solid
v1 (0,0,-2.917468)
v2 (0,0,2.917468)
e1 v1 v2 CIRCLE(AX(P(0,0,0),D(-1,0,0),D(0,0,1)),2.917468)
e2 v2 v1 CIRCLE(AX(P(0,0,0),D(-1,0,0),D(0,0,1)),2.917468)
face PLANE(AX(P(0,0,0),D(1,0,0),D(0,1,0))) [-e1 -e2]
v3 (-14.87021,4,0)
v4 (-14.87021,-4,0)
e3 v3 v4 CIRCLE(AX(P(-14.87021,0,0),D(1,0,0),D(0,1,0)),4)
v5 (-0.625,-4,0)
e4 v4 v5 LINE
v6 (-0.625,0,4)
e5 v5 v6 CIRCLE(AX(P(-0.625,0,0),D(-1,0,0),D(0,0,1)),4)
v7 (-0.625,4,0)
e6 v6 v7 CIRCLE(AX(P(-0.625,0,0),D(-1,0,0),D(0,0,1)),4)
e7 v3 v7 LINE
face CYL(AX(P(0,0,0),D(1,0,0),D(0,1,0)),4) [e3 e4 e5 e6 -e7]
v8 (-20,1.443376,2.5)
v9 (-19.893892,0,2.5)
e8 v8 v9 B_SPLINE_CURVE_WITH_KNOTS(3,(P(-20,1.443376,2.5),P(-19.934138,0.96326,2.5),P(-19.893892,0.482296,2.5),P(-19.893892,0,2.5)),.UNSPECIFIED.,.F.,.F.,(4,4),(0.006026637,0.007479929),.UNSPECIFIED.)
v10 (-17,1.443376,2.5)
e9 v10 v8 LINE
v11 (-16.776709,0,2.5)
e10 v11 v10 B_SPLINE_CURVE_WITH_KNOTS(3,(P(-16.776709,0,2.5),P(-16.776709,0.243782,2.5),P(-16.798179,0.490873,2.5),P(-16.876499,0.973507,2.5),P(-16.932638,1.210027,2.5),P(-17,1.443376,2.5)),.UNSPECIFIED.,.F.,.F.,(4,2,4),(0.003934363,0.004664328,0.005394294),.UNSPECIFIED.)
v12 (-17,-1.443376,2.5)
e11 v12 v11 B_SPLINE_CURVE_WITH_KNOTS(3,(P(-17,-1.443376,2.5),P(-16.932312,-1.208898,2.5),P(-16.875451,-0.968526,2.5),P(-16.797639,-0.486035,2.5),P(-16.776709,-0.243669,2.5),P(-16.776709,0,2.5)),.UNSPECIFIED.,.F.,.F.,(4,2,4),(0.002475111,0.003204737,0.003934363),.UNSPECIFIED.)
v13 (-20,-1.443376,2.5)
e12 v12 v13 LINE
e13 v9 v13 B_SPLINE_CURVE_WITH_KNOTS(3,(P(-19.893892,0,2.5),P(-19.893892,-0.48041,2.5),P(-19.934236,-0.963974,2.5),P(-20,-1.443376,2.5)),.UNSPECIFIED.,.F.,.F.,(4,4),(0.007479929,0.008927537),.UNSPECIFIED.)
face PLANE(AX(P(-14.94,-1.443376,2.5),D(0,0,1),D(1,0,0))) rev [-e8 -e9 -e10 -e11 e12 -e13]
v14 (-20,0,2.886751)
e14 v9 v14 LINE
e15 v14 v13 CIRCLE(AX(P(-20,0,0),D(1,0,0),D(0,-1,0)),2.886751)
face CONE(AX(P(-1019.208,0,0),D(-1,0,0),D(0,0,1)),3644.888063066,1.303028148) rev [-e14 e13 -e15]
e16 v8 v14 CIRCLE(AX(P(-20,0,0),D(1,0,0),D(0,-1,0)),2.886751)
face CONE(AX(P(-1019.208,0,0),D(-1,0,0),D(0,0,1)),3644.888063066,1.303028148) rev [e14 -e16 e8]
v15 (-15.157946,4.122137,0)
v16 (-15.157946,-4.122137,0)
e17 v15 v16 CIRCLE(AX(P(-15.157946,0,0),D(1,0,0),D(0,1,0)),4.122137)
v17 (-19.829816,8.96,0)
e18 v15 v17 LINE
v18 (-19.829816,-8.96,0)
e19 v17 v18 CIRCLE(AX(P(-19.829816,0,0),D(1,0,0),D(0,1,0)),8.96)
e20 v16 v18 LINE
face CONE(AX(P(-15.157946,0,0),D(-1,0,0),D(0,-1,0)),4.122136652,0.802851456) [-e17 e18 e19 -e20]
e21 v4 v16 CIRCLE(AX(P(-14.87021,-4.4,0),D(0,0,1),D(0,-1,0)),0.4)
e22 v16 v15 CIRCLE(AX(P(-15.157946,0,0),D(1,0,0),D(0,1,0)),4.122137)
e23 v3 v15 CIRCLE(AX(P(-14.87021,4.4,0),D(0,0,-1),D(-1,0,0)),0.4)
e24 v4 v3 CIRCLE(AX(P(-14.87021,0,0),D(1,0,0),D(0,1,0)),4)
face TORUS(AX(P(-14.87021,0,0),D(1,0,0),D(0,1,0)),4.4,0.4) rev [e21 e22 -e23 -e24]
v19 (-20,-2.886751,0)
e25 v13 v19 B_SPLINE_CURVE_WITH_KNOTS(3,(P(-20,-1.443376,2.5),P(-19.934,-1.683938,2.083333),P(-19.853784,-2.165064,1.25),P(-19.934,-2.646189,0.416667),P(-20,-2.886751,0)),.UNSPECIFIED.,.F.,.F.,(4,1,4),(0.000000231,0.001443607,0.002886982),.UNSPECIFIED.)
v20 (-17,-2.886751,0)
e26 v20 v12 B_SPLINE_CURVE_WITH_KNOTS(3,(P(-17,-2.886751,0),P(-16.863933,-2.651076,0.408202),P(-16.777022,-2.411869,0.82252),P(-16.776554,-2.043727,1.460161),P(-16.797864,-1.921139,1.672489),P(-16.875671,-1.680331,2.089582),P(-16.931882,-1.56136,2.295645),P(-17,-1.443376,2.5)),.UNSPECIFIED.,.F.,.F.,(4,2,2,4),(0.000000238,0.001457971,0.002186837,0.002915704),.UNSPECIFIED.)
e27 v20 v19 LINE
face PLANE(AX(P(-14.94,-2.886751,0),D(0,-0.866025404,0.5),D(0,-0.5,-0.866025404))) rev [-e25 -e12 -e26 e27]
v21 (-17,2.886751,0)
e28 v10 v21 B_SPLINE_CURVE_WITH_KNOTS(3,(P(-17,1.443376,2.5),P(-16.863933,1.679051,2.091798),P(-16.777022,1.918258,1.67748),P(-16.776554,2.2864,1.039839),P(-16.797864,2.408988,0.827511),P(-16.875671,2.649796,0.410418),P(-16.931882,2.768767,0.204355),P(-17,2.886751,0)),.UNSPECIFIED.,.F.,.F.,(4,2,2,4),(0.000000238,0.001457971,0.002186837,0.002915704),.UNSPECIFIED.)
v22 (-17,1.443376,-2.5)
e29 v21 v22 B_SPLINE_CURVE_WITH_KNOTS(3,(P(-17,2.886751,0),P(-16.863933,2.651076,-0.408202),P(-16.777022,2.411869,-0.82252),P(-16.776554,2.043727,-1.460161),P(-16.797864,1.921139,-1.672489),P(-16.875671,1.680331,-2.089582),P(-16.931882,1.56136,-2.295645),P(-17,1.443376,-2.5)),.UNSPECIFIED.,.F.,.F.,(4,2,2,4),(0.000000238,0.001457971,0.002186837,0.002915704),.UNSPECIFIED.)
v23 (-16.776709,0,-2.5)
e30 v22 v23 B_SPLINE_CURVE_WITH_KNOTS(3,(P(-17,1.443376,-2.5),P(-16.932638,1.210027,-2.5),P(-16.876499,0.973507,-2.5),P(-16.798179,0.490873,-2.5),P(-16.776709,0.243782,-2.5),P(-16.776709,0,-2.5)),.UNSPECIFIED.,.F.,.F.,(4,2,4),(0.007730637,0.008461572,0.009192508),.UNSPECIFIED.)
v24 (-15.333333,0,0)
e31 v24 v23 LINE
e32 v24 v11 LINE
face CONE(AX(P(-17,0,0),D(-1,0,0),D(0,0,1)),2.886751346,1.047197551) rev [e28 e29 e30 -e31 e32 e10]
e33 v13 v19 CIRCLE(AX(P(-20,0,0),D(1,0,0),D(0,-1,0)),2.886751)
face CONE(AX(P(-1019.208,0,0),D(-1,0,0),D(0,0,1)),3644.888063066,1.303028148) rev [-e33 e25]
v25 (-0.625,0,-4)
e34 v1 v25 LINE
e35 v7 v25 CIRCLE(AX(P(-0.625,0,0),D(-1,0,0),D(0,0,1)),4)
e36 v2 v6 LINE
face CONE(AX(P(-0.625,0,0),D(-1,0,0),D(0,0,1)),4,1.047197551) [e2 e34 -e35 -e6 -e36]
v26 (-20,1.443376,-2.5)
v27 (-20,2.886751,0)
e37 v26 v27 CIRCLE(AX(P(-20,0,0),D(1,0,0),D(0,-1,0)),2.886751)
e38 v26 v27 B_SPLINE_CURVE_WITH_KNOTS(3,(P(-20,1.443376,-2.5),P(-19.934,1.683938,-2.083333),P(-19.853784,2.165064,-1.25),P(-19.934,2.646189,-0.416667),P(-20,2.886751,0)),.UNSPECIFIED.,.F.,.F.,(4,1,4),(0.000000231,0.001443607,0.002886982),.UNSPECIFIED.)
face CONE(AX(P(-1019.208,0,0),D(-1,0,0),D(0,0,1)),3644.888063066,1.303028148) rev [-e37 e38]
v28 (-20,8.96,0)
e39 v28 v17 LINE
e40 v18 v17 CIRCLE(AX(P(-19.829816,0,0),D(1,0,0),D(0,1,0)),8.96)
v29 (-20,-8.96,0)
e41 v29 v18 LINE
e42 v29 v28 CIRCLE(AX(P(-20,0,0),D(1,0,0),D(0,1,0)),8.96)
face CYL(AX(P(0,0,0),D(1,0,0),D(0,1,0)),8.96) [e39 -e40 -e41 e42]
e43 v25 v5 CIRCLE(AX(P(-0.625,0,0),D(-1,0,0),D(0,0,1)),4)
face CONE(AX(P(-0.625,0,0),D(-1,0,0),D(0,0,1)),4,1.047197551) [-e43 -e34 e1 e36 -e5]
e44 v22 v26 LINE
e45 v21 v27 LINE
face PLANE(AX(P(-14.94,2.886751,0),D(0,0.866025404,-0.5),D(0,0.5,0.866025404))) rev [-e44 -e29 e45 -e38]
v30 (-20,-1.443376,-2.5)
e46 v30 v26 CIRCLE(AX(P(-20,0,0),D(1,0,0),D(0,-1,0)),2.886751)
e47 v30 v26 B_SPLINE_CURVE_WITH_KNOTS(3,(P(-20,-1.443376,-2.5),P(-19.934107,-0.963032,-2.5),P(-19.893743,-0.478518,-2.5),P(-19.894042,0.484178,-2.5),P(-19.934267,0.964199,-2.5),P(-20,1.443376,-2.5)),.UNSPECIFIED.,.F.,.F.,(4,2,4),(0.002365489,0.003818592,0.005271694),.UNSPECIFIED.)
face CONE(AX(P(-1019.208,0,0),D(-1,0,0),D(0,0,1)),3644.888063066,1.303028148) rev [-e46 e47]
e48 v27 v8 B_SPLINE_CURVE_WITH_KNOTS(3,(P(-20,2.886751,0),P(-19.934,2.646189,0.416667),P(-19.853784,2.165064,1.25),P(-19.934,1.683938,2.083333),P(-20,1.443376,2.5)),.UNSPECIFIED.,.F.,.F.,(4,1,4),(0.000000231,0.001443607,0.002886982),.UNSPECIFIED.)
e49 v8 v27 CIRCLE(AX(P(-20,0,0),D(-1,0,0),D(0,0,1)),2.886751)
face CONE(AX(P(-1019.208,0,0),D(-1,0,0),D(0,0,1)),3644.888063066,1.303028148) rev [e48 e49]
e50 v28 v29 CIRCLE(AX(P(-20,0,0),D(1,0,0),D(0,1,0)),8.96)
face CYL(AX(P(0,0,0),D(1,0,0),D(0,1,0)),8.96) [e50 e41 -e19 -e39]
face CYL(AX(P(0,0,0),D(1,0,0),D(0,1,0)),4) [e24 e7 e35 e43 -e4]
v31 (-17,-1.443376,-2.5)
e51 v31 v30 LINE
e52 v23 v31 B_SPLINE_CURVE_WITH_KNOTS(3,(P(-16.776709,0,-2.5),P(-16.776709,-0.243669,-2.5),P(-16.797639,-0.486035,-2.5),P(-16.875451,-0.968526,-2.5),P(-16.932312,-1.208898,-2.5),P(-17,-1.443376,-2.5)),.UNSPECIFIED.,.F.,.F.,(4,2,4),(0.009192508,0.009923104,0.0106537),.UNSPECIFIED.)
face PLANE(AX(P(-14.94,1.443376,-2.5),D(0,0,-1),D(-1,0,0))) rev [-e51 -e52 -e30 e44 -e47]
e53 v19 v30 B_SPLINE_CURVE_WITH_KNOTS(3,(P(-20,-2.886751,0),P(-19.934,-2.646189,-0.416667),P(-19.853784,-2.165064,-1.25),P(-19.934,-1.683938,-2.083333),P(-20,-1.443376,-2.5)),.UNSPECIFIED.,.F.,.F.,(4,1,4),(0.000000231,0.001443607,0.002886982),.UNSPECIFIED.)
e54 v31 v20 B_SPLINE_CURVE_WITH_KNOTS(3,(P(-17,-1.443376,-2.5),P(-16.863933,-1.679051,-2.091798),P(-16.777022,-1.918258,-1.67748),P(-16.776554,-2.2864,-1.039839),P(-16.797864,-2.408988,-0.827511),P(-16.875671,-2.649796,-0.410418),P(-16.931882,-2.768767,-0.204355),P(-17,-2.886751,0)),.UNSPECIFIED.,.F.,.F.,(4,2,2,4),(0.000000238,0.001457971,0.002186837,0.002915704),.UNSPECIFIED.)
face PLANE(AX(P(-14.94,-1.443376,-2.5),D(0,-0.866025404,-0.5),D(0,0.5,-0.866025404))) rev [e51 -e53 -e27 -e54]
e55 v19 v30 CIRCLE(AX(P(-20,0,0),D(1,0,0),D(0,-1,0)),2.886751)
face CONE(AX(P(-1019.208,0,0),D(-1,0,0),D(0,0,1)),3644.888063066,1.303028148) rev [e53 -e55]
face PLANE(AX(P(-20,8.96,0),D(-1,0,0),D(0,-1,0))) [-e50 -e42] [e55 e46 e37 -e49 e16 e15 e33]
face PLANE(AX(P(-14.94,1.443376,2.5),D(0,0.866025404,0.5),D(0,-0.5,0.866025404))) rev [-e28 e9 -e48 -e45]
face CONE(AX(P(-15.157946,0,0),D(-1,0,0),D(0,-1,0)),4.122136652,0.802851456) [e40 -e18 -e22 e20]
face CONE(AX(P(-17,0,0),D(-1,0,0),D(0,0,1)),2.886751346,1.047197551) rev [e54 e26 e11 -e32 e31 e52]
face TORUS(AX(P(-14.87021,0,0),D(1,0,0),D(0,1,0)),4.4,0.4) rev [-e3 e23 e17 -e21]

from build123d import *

# Parameters (mm, degrees)
CUT_EXTRUDE1_DEPTH = 5.06


with BuildPart() as part:
    # Sketch1 → Revolve1 (revolve)
    with BuildSketch(Plane.XY):
        with BuildLine():
            Line((0, 4), (-14.870210074, 4))
            ThreePointArc((-14.870210074, 4), (-15.026502525, 4.031798059), (-15.157945994, 4.122136652))
            Line((-15.157945994, 4.122136652), (-19.829816323, 8.96))
            Line((-19.829816323, 8.96), (-20, 8.96))
            Line((-20, 8.96), (-20, 0))
            Line((-20, 0), (0, 0))
            Line((0, 0), (0, 4))
        make_face()
    revolve(axis=Axis((0, 0, 0), (-1, 0, 0)))

    # Sketch2 → Cut-Extrude1 (cut)
    with BuildSketch(Plane.ZY.offset(20)):
        Polygon((0, 2.886751346), (-2.5, 1.443375673), (-2.5, -1.443375673), (0, -2.886751346), (2.5, -1.443375673), (2.5, 1.443375673), align=None)
    extrude(amount=-CUT_EXTRUDE1_DEPTH, mode=Mode.SUBTRACT)

    # Sketch6 → Revolve2 (revolve)
    with BuildSketch(Plane.XY, mode=Mode.PRIVATE) as revolve2_sk:
        Polygon((-17, 2.886751346), (-15.333333333, 0), (-14.22, 0), (-14.22, 2.886751346), align=None)
    revolve(revolve2_sk.sketch.rotate(Axis((-20, 0, 0), (1, 0, 0)), 90), axis=Axis((-20, 0, 0), (1, 0, 0)))

    # Sketch7 → Cut-Revolve2 (revolve, cut)
    with BuildSketch(Plane.XY):
        Polygon((-20, 2.886751346), (-20, 0), (-19.208, 0), align=None)
    revolve(axis=Axis((-20, 0, 0), (1, 0, 0)), mode=Mode.SUBTRACT)

    # Sketch4 → Cut-Revolve1 (revolve, cut)
    with BuildSketch(Plane.XY):
        Polygon((-0.625, 4), (0, 2.917468245), (0.625, 4), align=None)
    revolve(axis=Axis((-0.625, 0, 0), (1, 0, 0)), mode=Mode.SUBTRACT)


solid = part.part
